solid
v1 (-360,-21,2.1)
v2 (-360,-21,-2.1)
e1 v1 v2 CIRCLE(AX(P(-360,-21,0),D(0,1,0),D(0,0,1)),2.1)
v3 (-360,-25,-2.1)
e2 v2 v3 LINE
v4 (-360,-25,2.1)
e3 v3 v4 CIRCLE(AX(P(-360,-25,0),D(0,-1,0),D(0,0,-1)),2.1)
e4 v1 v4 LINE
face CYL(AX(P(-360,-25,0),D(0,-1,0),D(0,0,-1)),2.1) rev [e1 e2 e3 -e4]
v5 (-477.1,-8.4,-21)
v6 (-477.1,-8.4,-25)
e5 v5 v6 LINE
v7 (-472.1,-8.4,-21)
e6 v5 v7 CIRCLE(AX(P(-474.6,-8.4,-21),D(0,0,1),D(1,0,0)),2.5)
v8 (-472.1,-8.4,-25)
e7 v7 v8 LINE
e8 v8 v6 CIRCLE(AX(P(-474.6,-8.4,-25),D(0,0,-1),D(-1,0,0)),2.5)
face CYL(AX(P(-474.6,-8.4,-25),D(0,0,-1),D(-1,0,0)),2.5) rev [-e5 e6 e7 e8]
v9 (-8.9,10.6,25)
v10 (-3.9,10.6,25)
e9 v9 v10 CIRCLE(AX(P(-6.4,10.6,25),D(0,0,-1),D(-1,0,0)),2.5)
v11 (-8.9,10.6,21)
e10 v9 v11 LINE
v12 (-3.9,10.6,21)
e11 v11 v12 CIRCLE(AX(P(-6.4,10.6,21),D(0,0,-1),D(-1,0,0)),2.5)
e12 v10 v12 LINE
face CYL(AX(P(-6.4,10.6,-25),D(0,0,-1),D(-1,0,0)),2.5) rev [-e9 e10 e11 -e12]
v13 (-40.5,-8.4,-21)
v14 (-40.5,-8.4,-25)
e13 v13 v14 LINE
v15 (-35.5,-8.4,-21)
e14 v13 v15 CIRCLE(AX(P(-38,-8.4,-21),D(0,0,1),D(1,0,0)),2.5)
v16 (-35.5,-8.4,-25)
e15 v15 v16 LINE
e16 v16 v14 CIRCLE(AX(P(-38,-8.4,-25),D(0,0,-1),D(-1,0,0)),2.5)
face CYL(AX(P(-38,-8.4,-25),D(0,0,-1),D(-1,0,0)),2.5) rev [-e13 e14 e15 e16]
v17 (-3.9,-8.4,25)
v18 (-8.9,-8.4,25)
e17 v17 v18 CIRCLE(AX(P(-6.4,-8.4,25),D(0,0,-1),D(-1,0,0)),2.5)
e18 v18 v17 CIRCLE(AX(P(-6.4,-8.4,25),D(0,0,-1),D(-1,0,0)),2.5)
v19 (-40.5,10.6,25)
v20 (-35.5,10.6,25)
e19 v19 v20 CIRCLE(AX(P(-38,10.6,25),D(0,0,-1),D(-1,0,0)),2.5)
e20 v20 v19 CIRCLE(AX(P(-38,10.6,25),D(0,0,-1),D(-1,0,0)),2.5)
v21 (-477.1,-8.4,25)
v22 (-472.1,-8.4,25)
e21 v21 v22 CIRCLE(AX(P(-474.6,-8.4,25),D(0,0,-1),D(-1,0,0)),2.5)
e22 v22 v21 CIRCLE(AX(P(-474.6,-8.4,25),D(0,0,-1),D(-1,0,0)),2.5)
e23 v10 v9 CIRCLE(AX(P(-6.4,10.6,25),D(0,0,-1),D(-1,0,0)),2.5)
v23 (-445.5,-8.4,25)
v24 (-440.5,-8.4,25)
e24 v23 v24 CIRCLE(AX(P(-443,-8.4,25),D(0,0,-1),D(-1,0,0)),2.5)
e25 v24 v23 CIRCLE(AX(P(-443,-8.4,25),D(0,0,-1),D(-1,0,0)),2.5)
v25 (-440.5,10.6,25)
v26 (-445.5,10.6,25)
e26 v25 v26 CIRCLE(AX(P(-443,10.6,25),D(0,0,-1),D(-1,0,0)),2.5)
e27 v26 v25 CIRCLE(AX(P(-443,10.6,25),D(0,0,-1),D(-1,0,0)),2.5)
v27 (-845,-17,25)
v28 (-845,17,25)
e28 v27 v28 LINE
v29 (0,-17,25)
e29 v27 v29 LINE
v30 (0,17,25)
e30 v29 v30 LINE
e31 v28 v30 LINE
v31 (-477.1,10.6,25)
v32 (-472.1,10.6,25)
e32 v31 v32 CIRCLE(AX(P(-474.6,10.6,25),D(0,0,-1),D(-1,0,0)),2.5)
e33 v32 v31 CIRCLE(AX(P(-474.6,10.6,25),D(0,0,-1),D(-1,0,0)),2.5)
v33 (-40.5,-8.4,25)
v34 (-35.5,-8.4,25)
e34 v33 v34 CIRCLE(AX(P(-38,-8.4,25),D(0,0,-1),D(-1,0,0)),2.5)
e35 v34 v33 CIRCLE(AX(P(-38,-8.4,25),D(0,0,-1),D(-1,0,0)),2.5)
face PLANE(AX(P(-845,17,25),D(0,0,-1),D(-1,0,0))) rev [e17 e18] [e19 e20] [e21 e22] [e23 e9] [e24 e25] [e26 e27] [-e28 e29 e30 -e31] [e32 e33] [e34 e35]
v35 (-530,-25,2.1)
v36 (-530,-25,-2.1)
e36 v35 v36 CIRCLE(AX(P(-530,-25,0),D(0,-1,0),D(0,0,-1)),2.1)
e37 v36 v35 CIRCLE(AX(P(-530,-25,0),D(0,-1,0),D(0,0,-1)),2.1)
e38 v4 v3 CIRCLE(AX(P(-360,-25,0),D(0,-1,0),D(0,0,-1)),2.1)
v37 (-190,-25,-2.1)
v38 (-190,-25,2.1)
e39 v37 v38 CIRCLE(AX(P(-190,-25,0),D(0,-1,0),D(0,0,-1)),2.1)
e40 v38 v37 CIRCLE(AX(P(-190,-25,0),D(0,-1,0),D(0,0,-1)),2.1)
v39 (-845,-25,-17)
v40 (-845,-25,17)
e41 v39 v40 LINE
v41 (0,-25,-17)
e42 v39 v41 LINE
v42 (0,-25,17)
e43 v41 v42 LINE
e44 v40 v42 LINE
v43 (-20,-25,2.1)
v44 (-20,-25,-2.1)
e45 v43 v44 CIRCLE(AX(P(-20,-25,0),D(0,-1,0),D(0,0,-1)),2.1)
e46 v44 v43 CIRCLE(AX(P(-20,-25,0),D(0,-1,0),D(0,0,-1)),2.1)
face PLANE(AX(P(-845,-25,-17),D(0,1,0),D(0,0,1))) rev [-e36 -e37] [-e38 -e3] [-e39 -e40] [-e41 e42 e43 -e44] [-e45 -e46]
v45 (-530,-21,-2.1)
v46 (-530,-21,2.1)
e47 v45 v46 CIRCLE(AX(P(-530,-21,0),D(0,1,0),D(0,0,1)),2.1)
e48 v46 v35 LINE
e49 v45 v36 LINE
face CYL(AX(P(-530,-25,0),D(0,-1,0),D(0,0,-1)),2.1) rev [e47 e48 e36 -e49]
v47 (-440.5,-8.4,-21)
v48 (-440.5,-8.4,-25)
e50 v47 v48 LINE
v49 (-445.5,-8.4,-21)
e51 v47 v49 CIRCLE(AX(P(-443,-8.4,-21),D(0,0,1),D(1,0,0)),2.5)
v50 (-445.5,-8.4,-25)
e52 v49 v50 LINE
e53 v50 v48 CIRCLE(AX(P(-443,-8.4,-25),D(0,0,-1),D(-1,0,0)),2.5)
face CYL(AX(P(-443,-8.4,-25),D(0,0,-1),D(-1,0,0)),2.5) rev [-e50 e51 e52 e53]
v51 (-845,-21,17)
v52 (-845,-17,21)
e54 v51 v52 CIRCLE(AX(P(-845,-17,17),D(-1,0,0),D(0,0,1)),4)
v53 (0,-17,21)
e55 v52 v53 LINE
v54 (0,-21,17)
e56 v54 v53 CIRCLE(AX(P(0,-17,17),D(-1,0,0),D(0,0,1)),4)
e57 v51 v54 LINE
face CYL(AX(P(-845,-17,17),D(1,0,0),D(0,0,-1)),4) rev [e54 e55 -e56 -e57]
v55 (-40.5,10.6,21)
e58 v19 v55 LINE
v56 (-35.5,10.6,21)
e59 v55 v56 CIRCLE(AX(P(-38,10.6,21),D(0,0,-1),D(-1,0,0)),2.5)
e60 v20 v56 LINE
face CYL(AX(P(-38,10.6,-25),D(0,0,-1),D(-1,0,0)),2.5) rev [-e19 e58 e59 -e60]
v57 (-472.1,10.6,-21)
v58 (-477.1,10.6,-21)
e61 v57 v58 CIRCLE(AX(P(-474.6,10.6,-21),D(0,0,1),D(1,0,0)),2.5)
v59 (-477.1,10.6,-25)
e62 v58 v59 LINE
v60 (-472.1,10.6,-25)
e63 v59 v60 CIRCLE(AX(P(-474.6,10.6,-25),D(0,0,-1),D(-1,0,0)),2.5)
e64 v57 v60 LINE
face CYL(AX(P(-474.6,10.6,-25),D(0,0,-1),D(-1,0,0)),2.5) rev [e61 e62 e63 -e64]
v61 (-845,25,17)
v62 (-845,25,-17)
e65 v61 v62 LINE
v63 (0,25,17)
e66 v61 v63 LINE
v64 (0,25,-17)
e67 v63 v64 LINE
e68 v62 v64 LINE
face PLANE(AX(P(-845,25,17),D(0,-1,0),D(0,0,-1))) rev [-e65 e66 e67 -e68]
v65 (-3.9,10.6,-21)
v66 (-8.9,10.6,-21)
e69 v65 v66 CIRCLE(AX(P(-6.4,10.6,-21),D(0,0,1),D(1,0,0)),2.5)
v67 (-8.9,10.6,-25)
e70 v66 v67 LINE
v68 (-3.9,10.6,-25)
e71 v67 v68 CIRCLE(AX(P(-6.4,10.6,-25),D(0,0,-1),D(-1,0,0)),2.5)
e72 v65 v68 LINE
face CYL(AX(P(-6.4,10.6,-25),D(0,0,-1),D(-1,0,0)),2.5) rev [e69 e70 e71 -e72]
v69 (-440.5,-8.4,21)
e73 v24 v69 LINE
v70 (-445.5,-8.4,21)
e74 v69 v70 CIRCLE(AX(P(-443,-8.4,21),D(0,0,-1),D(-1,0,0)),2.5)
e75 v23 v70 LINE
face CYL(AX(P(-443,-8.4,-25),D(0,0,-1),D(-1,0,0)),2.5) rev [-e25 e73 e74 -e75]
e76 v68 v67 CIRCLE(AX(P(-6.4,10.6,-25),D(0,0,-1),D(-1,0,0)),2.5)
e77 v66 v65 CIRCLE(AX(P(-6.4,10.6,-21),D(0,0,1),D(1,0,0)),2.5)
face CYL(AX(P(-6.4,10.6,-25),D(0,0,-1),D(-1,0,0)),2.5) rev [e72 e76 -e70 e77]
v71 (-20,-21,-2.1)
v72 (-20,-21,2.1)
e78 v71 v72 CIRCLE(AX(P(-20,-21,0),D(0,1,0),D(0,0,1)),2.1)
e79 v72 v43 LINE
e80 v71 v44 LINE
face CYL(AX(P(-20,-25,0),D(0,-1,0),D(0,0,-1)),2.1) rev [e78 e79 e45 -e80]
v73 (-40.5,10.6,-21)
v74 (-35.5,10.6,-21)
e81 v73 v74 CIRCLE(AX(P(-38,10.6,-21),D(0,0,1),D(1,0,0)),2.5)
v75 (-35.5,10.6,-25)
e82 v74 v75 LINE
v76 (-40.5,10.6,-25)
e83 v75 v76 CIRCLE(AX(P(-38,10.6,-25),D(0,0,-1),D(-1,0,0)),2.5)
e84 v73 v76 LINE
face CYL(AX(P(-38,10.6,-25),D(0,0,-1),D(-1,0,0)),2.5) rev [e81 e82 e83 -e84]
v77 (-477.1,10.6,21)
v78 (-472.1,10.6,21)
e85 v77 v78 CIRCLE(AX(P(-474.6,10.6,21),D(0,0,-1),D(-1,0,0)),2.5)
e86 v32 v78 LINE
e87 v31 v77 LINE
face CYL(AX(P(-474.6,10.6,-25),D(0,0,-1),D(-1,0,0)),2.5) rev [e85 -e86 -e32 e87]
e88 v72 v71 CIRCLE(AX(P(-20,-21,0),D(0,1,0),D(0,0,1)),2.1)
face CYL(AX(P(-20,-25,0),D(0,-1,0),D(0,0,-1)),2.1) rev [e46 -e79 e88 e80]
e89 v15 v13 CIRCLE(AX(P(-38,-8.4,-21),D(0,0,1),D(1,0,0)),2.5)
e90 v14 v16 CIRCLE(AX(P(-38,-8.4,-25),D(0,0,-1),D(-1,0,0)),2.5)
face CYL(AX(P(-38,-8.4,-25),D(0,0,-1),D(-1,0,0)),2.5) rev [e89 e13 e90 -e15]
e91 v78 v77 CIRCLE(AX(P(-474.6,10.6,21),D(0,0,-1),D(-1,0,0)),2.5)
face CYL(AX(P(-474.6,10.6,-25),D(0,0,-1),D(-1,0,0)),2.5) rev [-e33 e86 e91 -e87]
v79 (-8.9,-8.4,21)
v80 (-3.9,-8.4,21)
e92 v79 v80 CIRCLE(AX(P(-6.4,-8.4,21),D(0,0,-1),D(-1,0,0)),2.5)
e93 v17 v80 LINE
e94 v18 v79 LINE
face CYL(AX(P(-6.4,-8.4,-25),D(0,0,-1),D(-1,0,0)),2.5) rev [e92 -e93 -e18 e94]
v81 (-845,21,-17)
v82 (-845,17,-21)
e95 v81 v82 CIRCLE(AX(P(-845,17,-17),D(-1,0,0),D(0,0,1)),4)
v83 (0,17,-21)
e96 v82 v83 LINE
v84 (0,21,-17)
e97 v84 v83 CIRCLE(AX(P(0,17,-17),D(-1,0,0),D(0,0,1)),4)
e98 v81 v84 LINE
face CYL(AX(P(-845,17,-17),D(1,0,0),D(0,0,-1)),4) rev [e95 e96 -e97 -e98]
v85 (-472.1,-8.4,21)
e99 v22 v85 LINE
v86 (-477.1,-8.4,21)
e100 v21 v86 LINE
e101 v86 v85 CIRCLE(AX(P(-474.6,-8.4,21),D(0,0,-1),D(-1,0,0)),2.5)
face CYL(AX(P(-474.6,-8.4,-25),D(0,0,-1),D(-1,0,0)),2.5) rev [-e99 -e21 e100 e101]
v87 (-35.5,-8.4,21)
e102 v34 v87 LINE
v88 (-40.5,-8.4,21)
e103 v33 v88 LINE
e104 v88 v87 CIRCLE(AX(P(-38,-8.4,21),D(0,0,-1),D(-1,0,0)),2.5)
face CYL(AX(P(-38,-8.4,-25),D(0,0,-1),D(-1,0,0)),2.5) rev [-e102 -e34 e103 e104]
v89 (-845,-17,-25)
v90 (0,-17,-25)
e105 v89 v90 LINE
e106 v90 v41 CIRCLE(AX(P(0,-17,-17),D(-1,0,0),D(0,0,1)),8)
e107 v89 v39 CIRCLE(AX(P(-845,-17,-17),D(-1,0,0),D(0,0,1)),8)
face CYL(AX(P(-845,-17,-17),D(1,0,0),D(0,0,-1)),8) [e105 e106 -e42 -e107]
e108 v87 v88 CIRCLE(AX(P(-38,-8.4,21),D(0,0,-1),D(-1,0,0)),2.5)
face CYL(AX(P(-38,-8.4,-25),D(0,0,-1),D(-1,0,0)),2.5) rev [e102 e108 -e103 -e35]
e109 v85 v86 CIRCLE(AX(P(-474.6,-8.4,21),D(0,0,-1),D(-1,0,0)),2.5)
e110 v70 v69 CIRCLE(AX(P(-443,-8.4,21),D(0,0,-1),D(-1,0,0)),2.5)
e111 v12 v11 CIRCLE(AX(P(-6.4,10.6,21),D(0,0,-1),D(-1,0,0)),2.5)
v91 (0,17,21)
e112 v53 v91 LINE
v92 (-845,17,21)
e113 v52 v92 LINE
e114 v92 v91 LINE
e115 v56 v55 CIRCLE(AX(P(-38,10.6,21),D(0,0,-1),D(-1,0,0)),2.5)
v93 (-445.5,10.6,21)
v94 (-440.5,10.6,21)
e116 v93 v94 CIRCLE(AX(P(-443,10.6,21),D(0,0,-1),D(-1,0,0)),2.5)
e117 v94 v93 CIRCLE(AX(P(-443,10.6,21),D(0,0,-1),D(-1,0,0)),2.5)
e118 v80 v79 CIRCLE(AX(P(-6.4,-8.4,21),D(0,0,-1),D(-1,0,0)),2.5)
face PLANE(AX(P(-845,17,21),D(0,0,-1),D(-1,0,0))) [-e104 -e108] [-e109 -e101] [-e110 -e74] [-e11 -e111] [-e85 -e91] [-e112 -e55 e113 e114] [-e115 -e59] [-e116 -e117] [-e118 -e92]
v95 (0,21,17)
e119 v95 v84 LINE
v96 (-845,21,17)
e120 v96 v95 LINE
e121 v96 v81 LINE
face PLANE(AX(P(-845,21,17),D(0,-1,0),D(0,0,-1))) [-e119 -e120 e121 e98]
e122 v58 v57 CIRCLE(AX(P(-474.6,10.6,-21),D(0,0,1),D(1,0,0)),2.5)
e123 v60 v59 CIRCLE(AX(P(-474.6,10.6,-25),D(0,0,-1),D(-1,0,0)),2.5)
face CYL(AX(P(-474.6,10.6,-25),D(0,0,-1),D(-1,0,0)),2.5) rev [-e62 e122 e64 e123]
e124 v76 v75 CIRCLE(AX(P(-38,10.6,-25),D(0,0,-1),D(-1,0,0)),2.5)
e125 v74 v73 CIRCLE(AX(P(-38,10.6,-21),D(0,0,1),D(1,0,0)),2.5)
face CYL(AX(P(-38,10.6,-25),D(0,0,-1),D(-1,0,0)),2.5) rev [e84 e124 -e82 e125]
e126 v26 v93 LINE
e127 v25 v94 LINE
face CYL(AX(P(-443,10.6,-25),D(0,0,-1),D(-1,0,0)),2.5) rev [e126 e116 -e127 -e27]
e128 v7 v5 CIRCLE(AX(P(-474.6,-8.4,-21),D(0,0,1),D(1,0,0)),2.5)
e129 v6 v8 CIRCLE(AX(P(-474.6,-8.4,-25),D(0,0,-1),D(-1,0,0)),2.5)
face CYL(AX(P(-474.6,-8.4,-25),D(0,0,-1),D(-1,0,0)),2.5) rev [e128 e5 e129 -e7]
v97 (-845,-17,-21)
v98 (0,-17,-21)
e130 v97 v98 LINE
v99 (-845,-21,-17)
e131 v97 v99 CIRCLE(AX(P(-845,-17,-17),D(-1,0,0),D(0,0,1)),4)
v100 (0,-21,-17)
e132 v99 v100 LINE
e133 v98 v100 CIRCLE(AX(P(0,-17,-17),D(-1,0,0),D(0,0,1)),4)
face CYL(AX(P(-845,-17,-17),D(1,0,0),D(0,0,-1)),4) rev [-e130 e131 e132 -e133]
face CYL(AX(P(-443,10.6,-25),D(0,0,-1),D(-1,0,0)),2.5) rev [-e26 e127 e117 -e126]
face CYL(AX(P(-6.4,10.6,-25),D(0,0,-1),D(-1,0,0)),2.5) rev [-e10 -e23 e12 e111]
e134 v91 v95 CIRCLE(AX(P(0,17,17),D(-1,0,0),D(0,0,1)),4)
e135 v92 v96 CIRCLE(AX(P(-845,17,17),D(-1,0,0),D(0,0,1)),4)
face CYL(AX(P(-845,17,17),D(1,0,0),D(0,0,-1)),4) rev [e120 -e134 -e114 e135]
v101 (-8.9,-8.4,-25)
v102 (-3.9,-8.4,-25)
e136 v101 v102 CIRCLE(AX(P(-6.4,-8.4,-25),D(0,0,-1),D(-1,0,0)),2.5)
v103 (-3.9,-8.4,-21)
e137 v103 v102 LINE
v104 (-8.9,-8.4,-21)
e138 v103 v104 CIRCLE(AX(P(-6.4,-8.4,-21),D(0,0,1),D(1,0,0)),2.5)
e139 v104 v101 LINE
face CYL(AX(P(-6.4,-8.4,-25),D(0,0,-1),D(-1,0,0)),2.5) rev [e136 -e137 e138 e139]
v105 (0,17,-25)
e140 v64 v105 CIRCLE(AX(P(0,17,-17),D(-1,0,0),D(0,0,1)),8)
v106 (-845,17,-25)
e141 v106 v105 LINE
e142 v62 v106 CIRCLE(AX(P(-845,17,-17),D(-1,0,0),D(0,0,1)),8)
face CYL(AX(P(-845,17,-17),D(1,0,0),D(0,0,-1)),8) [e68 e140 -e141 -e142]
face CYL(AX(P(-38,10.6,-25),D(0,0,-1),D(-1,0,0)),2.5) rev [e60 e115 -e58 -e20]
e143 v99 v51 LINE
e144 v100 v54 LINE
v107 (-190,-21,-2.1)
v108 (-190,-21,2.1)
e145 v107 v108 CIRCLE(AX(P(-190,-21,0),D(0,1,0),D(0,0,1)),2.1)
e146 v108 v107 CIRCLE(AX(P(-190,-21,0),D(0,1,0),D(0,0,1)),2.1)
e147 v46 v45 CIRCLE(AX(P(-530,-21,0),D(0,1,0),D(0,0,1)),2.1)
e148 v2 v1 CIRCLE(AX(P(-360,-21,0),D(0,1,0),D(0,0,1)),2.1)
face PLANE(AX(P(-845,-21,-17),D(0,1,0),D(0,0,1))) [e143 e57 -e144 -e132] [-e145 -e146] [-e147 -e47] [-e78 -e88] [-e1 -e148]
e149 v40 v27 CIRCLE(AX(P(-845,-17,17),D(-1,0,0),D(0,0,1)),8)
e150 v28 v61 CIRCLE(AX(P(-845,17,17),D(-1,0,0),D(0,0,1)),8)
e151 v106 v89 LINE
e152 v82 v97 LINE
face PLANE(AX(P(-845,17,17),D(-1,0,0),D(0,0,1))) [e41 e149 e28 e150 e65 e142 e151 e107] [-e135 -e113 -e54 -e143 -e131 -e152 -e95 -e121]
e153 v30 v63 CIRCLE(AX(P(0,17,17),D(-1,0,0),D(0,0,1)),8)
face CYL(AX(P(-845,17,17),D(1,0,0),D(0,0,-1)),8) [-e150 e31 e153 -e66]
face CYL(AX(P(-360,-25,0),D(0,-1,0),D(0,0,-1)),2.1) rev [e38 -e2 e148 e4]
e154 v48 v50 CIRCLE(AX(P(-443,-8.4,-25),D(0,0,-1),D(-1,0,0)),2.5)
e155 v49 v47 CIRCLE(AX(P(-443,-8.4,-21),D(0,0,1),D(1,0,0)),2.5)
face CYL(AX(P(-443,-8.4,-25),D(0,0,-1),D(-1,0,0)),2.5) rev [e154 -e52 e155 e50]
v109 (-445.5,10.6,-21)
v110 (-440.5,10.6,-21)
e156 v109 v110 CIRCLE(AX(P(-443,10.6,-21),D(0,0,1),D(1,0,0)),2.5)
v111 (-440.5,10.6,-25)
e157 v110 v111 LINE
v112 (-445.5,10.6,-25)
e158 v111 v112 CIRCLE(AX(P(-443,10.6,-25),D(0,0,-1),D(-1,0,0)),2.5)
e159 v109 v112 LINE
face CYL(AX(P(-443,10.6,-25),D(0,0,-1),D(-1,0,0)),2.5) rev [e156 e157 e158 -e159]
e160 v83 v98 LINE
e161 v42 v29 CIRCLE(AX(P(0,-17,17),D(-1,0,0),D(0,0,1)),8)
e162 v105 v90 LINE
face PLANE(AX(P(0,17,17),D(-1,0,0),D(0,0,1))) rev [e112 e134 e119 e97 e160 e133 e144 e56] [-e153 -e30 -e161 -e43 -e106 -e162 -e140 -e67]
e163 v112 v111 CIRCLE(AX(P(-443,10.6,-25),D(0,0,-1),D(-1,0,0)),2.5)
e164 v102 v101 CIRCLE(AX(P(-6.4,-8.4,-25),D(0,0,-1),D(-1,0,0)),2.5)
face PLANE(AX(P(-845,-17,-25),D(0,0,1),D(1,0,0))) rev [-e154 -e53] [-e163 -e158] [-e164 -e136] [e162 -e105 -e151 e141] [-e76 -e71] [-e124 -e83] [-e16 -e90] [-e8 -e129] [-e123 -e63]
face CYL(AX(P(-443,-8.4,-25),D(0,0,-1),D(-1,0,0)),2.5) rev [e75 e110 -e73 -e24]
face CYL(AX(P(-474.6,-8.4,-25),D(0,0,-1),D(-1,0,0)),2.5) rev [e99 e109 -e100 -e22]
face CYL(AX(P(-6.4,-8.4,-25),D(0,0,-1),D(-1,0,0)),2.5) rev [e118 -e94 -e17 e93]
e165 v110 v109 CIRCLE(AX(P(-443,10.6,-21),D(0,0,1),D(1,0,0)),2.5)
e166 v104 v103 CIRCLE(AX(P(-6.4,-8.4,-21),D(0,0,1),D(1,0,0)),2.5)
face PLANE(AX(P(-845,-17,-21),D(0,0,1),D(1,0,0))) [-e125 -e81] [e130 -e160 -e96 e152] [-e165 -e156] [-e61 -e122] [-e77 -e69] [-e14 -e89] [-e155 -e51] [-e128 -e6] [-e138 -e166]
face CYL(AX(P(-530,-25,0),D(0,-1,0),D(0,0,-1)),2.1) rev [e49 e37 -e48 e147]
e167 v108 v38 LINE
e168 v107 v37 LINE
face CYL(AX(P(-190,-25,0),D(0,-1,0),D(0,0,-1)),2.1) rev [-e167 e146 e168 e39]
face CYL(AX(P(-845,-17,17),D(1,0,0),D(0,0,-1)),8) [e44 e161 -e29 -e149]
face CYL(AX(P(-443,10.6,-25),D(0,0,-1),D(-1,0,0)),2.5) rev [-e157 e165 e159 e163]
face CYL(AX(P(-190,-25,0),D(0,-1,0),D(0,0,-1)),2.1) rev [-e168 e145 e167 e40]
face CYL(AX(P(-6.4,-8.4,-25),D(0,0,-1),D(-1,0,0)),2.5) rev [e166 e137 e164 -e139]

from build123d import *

# Parameters (mm, degrees)
GB_6728_1986_050_X_50_X_4_1_DEPTH = 845
HOLE_WIZARD_M6_1_D                = 5
HOLE_WIZARD_M5_1_D                = 4.2
HOLE_WIZARD_M5_1_DEPTH            = 4


with BuildPart() as part:
    # Sketch1 → Gb／6728-1986方形空心型钢 050 X 50 X 4(1) (new body)
    with BuildSketch(Plane.ZY):
        with BuildLine():
            Line((-17, -25), (17, -25))
            ThreePointArc((17, -25), (22.656854249, -22.656854249), (25, -17))
            Line((25, -17), (25, 17))
            ThreePointArc((25, 17), (22.656854249, 22.656854249), (17, 25))
            Line((17, 25), (-17, 25))
            ThreePointArc((-17, 25), (-22.656854249, 22.656854249), (-25, 17))
            Line((-25, 17), (-25, -17))
            ThreePointArc((-25, -17), (-22.656854249, -22.656854249), (-17, -25))
        make_face()
        with BuildLine():
            Line((-17, -21), (17, -21))
            ThreePointArc((17, -21), (19.828427125, -19.828427125), (21, -17))
            Line((21, -17), (21, 17))
            ThreePointArc((21, 17), (19.828427125, 19.828427125), (17, 21))
            Line((17, 21), (-17, 21))
            ThreePointArc((-17, 21), (-19.828427125, 19.828427125), (-21, 17))
            Line((-21, 17), (-21, -17))
            ThreePointArc((-21, -17), (-19.828427125, -19.828427125), (-17, -21))
        make_face(mode=Mode.SUBTRACT)
    extrude(amount=GB_6728_1986_050_X_50_X_4_1_DEPTH)

    # M6 螺纹孔1 (through all)
    with Locations(Plane(origin=(0, 0, -25), x_dir=(-1, 0, 0), z_dir=(0, 0, -1))):
        with Locations((6.4, 10.6), (6.4, -8.4), (38, 10.6), (38, -8.4), (443, 10.6), (443, -8.4), (474.6, 10.6), (474.6, -8.4)):
            Hole(HOLE_WIZARD_M6_1_D / 2)

    # M5 螺纹孔1
    with Locations(Plane(origin=(0, -25, 0), x_dir=(-1, 0, 0), z_dir=(0, -1, 0))):
        with Locations((20, 0), (190, 0), (360, 0), (530, 0)):
            Hole(HOLE_WIZARD_M5_1_D / 2, depth=HOLE_WIZARD_M5_1_DEPTH)


solid = part.part
